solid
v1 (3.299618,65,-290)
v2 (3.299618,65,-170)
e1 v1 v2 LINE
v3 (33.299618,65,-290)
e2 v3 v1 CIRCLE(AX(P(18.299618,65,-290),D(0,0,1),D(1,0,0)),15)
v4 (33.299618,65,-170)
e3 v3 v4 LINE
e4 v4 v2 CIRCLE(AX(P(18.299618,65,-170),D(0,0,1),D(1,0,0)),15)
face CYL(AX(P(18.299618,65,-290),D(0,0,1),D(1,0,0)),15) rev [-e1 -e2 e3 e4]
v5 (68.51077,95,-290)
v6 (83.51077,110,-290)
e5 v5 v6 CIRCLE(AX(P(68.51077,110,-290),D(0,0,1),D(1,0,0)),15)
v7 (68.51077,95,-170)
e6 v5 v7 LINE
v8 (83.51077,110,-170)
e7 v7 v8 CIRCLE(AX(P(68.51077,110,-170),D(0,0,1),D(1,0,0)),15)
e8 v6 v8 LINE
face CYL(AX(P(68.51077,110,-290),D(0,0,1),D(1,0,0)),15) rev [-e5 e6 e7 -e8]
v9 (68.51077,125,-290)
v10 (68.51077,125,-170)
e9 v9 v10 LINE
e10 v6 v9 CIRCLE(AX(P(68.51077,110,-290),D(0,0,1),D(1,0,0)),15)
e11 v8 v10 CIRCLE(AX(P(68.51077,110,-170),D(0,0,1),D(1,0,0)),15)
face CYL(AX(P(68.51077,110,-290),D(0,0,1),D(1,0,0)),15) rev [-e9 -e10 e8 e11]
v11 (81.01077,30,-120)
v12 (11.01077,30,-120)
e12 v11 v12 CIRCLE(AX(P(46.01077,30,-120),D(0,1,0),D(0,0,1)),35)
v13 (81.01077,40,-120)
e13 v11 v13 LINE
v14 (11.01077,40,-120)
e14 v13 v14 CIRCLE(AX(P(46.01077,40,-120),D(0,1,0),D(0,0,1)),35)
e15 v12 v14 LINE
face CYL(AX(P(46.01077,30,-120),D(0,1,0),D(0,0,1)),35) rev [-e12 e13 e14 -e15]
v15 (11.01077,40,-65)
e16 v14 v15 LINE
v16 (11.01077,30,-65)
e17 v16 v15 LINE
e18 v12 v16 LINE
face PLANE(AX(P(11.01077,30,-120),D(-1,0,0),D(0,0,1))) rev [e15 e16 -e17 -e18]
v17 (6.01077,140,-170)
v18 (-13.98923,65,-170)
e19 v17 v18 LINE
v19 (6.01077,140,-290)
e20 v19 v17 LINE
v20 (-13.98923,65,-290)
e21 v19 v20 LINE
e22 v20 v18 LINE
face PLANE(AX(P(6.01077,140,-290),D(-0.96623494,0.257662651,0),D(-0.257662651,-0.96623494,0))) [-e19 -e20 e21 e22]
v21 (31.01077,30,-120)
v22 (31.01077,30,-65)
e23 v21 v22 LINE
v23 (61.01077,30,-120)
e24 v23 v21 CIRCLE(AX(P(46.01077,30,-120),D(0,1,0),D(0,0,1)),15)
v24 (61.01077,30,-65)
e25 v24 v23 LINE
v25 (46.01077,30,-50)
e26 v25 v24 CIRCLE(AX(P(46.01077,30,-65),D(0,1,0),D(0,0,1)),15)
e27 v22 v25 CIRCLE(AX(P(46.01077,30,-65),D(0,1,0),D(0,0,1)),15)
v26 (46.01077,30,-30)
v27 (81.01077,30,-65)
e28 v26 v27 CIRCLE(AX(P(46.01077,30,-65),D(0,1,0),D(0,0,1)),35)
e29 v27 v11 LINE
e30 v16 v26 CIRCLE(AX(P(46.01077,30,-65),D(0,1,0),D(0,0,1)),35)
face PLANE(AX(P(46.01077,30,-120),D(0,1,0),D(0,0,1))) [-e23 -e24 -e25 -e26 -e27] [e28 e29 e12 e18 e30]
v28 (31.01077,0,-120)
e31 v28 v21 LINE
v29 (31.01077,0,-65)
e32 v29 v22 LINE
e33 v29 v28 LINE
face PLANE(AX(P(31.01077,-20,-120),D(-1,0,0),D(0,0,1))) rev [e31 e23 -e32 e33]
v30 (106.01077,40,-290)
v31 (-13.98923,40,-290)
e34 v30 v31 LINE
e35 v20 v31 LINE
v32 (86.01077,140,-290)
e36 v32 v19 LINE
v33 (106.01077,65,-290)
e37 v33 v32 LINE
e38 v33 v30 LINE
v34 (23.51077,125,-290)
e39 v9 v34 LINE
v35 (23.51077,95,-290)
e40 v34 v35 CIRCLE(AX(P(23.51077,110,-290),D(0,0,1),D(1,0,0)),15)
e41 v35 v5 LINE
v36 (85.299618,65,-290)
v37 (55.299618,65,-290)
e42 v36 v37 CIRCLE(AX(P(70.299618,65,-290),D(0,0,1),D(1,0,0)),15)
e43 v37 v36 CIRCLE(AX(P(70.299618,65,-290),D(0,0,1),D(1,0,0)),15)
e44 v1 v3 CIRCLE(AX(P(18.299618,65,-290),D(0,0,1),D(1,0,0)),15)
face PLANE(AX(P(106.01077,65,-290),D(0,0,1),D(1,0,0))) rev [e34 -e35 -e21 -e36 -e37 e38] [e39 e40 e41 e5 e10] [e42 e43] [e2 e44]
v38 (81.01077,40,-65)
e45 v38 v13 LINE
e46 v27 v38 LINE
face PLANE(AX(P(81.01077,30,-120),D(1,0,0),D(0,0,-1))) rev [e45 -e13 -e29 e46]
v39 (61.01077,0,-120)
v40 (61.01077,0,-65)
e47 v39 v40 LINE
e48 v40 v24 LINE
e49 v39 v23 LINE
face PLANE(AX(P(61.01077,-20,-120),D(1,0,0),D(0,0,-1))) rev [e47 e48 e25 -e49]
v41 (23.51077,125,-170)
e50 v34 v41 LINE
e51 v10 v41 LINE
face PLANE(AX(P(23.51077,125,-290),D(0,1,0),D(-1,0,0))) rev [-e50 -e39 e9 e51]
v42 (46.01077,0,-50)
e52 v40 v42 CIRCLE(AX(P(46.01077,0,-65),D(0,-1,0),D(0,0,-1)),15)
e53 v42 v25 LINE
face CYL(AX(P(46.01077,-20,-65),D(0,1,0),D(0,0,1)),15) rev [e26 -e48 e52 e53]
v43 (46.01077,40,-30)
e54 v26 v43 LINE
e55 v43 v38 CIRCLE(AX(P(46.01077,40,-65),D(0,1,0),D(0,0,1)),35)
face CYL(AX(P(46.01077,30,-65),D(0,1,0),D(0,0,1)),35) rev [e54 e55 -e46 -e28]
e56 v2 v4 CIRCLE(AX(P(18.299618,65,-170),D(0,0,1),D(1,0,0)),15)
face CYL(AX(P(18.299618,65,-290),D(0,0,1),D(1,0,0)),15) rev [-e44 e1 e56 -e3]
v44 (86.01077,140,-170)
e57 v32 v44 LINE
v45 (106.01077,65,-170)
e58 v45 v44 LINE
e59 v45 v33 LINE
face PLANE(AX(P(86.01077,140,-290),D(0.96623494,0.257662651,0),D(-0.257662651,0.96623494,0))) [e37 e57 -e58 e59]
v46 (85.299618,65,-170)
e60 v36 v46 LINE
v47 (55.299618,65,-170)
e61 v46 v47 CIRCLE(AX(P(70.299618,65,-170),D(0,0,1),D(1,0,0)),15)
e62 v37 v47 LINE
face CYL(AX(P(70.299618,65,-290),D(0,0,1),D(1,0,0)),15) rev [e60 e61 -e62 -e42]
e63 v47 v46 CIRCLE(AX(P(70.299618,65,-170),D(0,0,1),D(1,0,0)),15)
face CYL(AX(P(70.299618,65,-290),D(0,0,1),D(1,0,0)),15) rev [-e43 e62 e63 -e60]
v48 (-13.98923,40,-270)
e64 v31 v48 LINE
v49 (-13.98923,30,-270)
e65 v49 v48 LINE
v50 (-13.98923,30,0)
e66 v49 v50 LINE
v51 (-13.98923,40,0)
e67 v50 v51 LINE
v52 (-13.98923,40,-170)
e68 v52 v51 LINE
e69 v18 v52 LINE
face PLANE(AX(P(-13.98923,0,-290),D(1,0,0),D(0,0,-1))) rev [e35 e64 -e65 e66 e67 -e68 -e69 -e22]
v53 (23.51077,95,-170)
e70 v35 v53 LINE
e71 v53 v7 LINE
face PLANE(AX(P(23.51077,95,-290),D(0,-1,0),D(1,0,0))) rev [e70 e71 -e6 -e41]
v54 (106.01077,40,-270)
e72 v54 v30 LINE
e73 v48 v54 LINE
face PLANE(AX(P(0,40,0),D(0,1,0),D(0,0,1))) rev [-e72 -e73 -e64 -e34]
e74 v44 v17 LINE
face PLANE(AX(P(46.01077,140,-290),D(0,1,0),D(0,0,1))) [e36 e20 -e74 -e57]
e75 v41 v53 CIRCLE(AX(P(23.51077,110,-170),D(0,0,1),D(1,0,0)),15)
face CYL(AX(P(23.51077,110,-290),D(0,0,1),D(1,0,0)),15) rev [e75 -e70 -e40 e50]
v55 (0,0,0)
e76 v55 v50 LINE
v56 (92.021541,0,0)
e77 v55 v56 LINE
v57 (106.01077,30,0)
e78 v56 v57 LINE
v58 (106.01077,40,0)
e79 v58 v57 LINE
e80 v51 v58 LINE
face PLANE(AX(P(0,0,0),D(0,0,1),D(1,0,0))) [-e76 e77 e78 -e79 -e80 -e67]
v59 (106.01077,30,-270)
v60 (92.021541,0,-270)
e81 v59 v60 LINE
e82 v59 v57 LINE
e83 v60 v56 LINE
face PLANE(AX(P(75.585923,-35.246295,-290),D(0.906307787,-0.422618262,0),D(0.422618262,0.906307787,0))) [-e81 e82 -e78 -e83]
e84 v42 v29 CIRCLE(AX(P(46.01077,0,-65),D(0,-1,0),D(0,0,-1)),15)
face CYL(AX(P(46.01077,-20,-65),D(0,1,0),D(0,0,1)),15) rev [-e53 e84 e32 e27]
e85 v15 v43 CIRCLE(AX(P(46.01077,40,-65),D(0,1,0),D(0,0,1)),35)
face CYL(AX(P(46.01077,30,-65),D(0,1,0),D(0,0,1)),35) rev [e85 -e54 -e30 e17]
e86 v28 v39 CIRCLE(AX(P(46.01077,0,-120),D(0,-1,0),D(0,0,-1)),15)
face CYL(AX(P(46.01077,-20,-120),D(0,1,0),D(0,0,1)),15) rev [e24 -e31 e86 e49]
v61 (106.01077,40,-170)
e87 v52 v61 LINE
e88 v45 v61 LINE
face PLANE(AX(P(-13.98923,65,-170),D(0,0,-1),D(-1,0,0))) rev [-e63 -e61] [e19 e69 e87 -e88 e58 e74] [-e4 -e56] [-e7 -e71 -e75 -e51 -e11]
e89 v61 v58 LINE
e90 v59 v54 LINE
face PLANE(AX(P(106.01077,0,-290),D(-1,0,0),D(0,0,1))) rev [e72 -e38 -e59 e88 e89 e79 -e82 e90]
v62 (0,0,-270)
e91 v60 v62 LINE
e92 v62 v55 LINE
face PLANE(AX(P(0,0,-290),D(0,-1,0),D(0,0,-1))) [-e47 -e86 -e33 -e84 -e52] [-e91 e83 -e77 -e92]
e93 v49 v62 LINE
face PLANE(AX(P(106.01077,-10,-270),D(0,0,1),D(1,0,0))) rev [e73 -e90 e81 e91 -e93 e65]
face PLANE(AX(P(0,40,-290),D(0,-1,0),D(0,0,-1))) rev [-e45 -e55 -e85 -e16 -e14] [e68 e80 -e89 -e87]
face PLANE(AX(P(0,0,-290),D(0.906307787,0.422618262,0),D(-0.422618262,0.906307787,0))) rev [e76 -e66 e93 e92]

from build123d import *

# Parameters (mm, degrees)
DOVETAIL_BASE_SLIDE_DEPTH      = 290
SLOT_COUNTERBORE_10_DEEP_DEPTH = 10
ADJUSTING_SLOT_30_WIDE_DEPTH   = 50
RELIEF_CUT_SKETCH_W            = 120
RELIEF_CUT_SKETCH_H            = 20
RECTANGULAR_RELIEF_CUT_DEPTH   = 50
RAISED_PAD_SKETCH_W            = 120
RAISED_PAD_SKETCH_H            = 120
RAISED_PAD_25_DEPTH            = 25
UPRIGHT_HEAD_DEPTH             = 120
HEAD_THROUGH_SLOT_DEPTH        = 120
HEAD_HOLES_SKETCH_R            = 15
HEAD_HOLES_2X_30_DEPTH         = 120


with BuildPart() as part:
    # Dovetail Base Profile Sketch → Dovetail Base Slide (new body)
    with BuildSketch(Plane.XY):
        Polygon((106.010770255, 40), (106.010770255, 30), (92.021540511, 0), (0, 0), (-13.989229745, 30), (-13.989229745, 40), align=None)
    extrude(amount=-DOVETAIL_BASE_SLIDE_DEPTH)

    # Slot Counterbore Sketch → Slot Counterbore 10 Deep (cut)
    with BuildSketch(Plane(origin=(0, 40, 0), x_dir=(1, 0, 0), z_dir=(0, 1, 0))):
        with BuildLine():
            Line((11.010770255, 120), (11.010770255, 65))
            ThreePointArc((11.010770255, 65), (46.010770255, 30), (81.010770255, 65))
            Line((81.010770255, 65), (81.010770255, 120))
            ThreePointArc((81.010770255, 120), (46.010770255, 155), (11.010770255, 120))
        make_face()
    extrude(amount=-SLOT_COUNTERBORE_10_DEEP_DEPTH, mode=Mode.SUBTRACT)

    # Adjusting Slot Sketch → Adjusting Slot 30 Wide (cut)
    with BuildSketch(Plane(origin=(0, 30, 0), x_dir=(1, 0, 0), z_dir=(0, 1, 0))):
        with BuildLine():
            Line((31.010770255, 120), (31.010770255, 65))
            ThreePointArc((31.010770255, 65), (46.010770255, 50), (61.010770255, 65))
            Line((61.010770255, 65), (61.010770255, 120))
            ThreePointArc((61.010770255, 120), (46.010770255, 135), (31.010770255, 120))
        make_face()
    extrude(amount=-ADJUSTING_SLOT_30_WIDE_DEPTH, mode=Mode.SUBTRACT)

    # Relief Cut Sketch → Rectangular Relief Cut (cut)
    with BuildSketch(Plane(origin=(0, 40, 0), x_dir=(1, 0, 0), z_dir=(0, 1, 0))):
        with Locations((46.010770255, 280)):
            Rectangle(RELIEF_CUT_SKETCH_W, RELIEF_CUT_SKETCH_H)
    extrude(amount=-RECTANGULAR_RELIEF_CUT_DEPTH, mode=Mode.SUBTRACT)

    # Raised Pad Sketch → Raised Pad 25 (add)
    with BuildSketch(Plane(origin=(0, 40, 0), x_dir=(1, 0, 0), z_dir=(0, 1, 0))):
        with Locations((46.010770255, 230)):
            Rectangle(RAISED_PAD_SKETCH_W, RAISED_PAD_SKETCH_H)
    extrude(amount=RAISED_PAD_25_DEPTH)

    # Upright Head Profile Sketch → Upright Head (add)
    with BuildSketch(Plane.XY.offset(-170)):
        Polygon((46.010770255, 140), (6.010770255, 140), (-13.989229745, 65), (106.010770255, 65), (86.010770255, 140), align=None)
    extrude(amount=-UPRIGHT_HEAD_DEPTH)

    # Head Slot Sketch → Head Through Slot (cut)
    with BuildSketch(Plane.XY.offset(-170)):
        with BuildLine():
            Line((23.510770255, 125), (68.510770255, 125))
            ThreePointArc((68.510770255, 125), (83.510770255, 110), (68.510770255, 95))
            Line((68.510770255, 95), (23.510770255, 95))
            ThreePointArc((23.510770255, 95), (8.510770255, 110), (23.510770255, 125))
        make_face()
    extrude(amount=-HEAD_THROUGH_SLOT_DEPTH, mode=Mode.SUBTRACT)

    # Head Holes Sketch → Head Holes 2xØ30 (cut)
    with BuildSketch(Plane.XY.offset(-170)):
        with Locations((18.299617998, 65)):
            Circle(HEAD_HOLES_SKETCH_R)
        with Locations((70.299617998, 65)):
            Circle(HEAD_HOLES_SKETCH_R)
    extrude(amount=-HEAD_HOLES_2X_30_DEPTH, mode=Mode.SUBTRACT)


solid = part.part
